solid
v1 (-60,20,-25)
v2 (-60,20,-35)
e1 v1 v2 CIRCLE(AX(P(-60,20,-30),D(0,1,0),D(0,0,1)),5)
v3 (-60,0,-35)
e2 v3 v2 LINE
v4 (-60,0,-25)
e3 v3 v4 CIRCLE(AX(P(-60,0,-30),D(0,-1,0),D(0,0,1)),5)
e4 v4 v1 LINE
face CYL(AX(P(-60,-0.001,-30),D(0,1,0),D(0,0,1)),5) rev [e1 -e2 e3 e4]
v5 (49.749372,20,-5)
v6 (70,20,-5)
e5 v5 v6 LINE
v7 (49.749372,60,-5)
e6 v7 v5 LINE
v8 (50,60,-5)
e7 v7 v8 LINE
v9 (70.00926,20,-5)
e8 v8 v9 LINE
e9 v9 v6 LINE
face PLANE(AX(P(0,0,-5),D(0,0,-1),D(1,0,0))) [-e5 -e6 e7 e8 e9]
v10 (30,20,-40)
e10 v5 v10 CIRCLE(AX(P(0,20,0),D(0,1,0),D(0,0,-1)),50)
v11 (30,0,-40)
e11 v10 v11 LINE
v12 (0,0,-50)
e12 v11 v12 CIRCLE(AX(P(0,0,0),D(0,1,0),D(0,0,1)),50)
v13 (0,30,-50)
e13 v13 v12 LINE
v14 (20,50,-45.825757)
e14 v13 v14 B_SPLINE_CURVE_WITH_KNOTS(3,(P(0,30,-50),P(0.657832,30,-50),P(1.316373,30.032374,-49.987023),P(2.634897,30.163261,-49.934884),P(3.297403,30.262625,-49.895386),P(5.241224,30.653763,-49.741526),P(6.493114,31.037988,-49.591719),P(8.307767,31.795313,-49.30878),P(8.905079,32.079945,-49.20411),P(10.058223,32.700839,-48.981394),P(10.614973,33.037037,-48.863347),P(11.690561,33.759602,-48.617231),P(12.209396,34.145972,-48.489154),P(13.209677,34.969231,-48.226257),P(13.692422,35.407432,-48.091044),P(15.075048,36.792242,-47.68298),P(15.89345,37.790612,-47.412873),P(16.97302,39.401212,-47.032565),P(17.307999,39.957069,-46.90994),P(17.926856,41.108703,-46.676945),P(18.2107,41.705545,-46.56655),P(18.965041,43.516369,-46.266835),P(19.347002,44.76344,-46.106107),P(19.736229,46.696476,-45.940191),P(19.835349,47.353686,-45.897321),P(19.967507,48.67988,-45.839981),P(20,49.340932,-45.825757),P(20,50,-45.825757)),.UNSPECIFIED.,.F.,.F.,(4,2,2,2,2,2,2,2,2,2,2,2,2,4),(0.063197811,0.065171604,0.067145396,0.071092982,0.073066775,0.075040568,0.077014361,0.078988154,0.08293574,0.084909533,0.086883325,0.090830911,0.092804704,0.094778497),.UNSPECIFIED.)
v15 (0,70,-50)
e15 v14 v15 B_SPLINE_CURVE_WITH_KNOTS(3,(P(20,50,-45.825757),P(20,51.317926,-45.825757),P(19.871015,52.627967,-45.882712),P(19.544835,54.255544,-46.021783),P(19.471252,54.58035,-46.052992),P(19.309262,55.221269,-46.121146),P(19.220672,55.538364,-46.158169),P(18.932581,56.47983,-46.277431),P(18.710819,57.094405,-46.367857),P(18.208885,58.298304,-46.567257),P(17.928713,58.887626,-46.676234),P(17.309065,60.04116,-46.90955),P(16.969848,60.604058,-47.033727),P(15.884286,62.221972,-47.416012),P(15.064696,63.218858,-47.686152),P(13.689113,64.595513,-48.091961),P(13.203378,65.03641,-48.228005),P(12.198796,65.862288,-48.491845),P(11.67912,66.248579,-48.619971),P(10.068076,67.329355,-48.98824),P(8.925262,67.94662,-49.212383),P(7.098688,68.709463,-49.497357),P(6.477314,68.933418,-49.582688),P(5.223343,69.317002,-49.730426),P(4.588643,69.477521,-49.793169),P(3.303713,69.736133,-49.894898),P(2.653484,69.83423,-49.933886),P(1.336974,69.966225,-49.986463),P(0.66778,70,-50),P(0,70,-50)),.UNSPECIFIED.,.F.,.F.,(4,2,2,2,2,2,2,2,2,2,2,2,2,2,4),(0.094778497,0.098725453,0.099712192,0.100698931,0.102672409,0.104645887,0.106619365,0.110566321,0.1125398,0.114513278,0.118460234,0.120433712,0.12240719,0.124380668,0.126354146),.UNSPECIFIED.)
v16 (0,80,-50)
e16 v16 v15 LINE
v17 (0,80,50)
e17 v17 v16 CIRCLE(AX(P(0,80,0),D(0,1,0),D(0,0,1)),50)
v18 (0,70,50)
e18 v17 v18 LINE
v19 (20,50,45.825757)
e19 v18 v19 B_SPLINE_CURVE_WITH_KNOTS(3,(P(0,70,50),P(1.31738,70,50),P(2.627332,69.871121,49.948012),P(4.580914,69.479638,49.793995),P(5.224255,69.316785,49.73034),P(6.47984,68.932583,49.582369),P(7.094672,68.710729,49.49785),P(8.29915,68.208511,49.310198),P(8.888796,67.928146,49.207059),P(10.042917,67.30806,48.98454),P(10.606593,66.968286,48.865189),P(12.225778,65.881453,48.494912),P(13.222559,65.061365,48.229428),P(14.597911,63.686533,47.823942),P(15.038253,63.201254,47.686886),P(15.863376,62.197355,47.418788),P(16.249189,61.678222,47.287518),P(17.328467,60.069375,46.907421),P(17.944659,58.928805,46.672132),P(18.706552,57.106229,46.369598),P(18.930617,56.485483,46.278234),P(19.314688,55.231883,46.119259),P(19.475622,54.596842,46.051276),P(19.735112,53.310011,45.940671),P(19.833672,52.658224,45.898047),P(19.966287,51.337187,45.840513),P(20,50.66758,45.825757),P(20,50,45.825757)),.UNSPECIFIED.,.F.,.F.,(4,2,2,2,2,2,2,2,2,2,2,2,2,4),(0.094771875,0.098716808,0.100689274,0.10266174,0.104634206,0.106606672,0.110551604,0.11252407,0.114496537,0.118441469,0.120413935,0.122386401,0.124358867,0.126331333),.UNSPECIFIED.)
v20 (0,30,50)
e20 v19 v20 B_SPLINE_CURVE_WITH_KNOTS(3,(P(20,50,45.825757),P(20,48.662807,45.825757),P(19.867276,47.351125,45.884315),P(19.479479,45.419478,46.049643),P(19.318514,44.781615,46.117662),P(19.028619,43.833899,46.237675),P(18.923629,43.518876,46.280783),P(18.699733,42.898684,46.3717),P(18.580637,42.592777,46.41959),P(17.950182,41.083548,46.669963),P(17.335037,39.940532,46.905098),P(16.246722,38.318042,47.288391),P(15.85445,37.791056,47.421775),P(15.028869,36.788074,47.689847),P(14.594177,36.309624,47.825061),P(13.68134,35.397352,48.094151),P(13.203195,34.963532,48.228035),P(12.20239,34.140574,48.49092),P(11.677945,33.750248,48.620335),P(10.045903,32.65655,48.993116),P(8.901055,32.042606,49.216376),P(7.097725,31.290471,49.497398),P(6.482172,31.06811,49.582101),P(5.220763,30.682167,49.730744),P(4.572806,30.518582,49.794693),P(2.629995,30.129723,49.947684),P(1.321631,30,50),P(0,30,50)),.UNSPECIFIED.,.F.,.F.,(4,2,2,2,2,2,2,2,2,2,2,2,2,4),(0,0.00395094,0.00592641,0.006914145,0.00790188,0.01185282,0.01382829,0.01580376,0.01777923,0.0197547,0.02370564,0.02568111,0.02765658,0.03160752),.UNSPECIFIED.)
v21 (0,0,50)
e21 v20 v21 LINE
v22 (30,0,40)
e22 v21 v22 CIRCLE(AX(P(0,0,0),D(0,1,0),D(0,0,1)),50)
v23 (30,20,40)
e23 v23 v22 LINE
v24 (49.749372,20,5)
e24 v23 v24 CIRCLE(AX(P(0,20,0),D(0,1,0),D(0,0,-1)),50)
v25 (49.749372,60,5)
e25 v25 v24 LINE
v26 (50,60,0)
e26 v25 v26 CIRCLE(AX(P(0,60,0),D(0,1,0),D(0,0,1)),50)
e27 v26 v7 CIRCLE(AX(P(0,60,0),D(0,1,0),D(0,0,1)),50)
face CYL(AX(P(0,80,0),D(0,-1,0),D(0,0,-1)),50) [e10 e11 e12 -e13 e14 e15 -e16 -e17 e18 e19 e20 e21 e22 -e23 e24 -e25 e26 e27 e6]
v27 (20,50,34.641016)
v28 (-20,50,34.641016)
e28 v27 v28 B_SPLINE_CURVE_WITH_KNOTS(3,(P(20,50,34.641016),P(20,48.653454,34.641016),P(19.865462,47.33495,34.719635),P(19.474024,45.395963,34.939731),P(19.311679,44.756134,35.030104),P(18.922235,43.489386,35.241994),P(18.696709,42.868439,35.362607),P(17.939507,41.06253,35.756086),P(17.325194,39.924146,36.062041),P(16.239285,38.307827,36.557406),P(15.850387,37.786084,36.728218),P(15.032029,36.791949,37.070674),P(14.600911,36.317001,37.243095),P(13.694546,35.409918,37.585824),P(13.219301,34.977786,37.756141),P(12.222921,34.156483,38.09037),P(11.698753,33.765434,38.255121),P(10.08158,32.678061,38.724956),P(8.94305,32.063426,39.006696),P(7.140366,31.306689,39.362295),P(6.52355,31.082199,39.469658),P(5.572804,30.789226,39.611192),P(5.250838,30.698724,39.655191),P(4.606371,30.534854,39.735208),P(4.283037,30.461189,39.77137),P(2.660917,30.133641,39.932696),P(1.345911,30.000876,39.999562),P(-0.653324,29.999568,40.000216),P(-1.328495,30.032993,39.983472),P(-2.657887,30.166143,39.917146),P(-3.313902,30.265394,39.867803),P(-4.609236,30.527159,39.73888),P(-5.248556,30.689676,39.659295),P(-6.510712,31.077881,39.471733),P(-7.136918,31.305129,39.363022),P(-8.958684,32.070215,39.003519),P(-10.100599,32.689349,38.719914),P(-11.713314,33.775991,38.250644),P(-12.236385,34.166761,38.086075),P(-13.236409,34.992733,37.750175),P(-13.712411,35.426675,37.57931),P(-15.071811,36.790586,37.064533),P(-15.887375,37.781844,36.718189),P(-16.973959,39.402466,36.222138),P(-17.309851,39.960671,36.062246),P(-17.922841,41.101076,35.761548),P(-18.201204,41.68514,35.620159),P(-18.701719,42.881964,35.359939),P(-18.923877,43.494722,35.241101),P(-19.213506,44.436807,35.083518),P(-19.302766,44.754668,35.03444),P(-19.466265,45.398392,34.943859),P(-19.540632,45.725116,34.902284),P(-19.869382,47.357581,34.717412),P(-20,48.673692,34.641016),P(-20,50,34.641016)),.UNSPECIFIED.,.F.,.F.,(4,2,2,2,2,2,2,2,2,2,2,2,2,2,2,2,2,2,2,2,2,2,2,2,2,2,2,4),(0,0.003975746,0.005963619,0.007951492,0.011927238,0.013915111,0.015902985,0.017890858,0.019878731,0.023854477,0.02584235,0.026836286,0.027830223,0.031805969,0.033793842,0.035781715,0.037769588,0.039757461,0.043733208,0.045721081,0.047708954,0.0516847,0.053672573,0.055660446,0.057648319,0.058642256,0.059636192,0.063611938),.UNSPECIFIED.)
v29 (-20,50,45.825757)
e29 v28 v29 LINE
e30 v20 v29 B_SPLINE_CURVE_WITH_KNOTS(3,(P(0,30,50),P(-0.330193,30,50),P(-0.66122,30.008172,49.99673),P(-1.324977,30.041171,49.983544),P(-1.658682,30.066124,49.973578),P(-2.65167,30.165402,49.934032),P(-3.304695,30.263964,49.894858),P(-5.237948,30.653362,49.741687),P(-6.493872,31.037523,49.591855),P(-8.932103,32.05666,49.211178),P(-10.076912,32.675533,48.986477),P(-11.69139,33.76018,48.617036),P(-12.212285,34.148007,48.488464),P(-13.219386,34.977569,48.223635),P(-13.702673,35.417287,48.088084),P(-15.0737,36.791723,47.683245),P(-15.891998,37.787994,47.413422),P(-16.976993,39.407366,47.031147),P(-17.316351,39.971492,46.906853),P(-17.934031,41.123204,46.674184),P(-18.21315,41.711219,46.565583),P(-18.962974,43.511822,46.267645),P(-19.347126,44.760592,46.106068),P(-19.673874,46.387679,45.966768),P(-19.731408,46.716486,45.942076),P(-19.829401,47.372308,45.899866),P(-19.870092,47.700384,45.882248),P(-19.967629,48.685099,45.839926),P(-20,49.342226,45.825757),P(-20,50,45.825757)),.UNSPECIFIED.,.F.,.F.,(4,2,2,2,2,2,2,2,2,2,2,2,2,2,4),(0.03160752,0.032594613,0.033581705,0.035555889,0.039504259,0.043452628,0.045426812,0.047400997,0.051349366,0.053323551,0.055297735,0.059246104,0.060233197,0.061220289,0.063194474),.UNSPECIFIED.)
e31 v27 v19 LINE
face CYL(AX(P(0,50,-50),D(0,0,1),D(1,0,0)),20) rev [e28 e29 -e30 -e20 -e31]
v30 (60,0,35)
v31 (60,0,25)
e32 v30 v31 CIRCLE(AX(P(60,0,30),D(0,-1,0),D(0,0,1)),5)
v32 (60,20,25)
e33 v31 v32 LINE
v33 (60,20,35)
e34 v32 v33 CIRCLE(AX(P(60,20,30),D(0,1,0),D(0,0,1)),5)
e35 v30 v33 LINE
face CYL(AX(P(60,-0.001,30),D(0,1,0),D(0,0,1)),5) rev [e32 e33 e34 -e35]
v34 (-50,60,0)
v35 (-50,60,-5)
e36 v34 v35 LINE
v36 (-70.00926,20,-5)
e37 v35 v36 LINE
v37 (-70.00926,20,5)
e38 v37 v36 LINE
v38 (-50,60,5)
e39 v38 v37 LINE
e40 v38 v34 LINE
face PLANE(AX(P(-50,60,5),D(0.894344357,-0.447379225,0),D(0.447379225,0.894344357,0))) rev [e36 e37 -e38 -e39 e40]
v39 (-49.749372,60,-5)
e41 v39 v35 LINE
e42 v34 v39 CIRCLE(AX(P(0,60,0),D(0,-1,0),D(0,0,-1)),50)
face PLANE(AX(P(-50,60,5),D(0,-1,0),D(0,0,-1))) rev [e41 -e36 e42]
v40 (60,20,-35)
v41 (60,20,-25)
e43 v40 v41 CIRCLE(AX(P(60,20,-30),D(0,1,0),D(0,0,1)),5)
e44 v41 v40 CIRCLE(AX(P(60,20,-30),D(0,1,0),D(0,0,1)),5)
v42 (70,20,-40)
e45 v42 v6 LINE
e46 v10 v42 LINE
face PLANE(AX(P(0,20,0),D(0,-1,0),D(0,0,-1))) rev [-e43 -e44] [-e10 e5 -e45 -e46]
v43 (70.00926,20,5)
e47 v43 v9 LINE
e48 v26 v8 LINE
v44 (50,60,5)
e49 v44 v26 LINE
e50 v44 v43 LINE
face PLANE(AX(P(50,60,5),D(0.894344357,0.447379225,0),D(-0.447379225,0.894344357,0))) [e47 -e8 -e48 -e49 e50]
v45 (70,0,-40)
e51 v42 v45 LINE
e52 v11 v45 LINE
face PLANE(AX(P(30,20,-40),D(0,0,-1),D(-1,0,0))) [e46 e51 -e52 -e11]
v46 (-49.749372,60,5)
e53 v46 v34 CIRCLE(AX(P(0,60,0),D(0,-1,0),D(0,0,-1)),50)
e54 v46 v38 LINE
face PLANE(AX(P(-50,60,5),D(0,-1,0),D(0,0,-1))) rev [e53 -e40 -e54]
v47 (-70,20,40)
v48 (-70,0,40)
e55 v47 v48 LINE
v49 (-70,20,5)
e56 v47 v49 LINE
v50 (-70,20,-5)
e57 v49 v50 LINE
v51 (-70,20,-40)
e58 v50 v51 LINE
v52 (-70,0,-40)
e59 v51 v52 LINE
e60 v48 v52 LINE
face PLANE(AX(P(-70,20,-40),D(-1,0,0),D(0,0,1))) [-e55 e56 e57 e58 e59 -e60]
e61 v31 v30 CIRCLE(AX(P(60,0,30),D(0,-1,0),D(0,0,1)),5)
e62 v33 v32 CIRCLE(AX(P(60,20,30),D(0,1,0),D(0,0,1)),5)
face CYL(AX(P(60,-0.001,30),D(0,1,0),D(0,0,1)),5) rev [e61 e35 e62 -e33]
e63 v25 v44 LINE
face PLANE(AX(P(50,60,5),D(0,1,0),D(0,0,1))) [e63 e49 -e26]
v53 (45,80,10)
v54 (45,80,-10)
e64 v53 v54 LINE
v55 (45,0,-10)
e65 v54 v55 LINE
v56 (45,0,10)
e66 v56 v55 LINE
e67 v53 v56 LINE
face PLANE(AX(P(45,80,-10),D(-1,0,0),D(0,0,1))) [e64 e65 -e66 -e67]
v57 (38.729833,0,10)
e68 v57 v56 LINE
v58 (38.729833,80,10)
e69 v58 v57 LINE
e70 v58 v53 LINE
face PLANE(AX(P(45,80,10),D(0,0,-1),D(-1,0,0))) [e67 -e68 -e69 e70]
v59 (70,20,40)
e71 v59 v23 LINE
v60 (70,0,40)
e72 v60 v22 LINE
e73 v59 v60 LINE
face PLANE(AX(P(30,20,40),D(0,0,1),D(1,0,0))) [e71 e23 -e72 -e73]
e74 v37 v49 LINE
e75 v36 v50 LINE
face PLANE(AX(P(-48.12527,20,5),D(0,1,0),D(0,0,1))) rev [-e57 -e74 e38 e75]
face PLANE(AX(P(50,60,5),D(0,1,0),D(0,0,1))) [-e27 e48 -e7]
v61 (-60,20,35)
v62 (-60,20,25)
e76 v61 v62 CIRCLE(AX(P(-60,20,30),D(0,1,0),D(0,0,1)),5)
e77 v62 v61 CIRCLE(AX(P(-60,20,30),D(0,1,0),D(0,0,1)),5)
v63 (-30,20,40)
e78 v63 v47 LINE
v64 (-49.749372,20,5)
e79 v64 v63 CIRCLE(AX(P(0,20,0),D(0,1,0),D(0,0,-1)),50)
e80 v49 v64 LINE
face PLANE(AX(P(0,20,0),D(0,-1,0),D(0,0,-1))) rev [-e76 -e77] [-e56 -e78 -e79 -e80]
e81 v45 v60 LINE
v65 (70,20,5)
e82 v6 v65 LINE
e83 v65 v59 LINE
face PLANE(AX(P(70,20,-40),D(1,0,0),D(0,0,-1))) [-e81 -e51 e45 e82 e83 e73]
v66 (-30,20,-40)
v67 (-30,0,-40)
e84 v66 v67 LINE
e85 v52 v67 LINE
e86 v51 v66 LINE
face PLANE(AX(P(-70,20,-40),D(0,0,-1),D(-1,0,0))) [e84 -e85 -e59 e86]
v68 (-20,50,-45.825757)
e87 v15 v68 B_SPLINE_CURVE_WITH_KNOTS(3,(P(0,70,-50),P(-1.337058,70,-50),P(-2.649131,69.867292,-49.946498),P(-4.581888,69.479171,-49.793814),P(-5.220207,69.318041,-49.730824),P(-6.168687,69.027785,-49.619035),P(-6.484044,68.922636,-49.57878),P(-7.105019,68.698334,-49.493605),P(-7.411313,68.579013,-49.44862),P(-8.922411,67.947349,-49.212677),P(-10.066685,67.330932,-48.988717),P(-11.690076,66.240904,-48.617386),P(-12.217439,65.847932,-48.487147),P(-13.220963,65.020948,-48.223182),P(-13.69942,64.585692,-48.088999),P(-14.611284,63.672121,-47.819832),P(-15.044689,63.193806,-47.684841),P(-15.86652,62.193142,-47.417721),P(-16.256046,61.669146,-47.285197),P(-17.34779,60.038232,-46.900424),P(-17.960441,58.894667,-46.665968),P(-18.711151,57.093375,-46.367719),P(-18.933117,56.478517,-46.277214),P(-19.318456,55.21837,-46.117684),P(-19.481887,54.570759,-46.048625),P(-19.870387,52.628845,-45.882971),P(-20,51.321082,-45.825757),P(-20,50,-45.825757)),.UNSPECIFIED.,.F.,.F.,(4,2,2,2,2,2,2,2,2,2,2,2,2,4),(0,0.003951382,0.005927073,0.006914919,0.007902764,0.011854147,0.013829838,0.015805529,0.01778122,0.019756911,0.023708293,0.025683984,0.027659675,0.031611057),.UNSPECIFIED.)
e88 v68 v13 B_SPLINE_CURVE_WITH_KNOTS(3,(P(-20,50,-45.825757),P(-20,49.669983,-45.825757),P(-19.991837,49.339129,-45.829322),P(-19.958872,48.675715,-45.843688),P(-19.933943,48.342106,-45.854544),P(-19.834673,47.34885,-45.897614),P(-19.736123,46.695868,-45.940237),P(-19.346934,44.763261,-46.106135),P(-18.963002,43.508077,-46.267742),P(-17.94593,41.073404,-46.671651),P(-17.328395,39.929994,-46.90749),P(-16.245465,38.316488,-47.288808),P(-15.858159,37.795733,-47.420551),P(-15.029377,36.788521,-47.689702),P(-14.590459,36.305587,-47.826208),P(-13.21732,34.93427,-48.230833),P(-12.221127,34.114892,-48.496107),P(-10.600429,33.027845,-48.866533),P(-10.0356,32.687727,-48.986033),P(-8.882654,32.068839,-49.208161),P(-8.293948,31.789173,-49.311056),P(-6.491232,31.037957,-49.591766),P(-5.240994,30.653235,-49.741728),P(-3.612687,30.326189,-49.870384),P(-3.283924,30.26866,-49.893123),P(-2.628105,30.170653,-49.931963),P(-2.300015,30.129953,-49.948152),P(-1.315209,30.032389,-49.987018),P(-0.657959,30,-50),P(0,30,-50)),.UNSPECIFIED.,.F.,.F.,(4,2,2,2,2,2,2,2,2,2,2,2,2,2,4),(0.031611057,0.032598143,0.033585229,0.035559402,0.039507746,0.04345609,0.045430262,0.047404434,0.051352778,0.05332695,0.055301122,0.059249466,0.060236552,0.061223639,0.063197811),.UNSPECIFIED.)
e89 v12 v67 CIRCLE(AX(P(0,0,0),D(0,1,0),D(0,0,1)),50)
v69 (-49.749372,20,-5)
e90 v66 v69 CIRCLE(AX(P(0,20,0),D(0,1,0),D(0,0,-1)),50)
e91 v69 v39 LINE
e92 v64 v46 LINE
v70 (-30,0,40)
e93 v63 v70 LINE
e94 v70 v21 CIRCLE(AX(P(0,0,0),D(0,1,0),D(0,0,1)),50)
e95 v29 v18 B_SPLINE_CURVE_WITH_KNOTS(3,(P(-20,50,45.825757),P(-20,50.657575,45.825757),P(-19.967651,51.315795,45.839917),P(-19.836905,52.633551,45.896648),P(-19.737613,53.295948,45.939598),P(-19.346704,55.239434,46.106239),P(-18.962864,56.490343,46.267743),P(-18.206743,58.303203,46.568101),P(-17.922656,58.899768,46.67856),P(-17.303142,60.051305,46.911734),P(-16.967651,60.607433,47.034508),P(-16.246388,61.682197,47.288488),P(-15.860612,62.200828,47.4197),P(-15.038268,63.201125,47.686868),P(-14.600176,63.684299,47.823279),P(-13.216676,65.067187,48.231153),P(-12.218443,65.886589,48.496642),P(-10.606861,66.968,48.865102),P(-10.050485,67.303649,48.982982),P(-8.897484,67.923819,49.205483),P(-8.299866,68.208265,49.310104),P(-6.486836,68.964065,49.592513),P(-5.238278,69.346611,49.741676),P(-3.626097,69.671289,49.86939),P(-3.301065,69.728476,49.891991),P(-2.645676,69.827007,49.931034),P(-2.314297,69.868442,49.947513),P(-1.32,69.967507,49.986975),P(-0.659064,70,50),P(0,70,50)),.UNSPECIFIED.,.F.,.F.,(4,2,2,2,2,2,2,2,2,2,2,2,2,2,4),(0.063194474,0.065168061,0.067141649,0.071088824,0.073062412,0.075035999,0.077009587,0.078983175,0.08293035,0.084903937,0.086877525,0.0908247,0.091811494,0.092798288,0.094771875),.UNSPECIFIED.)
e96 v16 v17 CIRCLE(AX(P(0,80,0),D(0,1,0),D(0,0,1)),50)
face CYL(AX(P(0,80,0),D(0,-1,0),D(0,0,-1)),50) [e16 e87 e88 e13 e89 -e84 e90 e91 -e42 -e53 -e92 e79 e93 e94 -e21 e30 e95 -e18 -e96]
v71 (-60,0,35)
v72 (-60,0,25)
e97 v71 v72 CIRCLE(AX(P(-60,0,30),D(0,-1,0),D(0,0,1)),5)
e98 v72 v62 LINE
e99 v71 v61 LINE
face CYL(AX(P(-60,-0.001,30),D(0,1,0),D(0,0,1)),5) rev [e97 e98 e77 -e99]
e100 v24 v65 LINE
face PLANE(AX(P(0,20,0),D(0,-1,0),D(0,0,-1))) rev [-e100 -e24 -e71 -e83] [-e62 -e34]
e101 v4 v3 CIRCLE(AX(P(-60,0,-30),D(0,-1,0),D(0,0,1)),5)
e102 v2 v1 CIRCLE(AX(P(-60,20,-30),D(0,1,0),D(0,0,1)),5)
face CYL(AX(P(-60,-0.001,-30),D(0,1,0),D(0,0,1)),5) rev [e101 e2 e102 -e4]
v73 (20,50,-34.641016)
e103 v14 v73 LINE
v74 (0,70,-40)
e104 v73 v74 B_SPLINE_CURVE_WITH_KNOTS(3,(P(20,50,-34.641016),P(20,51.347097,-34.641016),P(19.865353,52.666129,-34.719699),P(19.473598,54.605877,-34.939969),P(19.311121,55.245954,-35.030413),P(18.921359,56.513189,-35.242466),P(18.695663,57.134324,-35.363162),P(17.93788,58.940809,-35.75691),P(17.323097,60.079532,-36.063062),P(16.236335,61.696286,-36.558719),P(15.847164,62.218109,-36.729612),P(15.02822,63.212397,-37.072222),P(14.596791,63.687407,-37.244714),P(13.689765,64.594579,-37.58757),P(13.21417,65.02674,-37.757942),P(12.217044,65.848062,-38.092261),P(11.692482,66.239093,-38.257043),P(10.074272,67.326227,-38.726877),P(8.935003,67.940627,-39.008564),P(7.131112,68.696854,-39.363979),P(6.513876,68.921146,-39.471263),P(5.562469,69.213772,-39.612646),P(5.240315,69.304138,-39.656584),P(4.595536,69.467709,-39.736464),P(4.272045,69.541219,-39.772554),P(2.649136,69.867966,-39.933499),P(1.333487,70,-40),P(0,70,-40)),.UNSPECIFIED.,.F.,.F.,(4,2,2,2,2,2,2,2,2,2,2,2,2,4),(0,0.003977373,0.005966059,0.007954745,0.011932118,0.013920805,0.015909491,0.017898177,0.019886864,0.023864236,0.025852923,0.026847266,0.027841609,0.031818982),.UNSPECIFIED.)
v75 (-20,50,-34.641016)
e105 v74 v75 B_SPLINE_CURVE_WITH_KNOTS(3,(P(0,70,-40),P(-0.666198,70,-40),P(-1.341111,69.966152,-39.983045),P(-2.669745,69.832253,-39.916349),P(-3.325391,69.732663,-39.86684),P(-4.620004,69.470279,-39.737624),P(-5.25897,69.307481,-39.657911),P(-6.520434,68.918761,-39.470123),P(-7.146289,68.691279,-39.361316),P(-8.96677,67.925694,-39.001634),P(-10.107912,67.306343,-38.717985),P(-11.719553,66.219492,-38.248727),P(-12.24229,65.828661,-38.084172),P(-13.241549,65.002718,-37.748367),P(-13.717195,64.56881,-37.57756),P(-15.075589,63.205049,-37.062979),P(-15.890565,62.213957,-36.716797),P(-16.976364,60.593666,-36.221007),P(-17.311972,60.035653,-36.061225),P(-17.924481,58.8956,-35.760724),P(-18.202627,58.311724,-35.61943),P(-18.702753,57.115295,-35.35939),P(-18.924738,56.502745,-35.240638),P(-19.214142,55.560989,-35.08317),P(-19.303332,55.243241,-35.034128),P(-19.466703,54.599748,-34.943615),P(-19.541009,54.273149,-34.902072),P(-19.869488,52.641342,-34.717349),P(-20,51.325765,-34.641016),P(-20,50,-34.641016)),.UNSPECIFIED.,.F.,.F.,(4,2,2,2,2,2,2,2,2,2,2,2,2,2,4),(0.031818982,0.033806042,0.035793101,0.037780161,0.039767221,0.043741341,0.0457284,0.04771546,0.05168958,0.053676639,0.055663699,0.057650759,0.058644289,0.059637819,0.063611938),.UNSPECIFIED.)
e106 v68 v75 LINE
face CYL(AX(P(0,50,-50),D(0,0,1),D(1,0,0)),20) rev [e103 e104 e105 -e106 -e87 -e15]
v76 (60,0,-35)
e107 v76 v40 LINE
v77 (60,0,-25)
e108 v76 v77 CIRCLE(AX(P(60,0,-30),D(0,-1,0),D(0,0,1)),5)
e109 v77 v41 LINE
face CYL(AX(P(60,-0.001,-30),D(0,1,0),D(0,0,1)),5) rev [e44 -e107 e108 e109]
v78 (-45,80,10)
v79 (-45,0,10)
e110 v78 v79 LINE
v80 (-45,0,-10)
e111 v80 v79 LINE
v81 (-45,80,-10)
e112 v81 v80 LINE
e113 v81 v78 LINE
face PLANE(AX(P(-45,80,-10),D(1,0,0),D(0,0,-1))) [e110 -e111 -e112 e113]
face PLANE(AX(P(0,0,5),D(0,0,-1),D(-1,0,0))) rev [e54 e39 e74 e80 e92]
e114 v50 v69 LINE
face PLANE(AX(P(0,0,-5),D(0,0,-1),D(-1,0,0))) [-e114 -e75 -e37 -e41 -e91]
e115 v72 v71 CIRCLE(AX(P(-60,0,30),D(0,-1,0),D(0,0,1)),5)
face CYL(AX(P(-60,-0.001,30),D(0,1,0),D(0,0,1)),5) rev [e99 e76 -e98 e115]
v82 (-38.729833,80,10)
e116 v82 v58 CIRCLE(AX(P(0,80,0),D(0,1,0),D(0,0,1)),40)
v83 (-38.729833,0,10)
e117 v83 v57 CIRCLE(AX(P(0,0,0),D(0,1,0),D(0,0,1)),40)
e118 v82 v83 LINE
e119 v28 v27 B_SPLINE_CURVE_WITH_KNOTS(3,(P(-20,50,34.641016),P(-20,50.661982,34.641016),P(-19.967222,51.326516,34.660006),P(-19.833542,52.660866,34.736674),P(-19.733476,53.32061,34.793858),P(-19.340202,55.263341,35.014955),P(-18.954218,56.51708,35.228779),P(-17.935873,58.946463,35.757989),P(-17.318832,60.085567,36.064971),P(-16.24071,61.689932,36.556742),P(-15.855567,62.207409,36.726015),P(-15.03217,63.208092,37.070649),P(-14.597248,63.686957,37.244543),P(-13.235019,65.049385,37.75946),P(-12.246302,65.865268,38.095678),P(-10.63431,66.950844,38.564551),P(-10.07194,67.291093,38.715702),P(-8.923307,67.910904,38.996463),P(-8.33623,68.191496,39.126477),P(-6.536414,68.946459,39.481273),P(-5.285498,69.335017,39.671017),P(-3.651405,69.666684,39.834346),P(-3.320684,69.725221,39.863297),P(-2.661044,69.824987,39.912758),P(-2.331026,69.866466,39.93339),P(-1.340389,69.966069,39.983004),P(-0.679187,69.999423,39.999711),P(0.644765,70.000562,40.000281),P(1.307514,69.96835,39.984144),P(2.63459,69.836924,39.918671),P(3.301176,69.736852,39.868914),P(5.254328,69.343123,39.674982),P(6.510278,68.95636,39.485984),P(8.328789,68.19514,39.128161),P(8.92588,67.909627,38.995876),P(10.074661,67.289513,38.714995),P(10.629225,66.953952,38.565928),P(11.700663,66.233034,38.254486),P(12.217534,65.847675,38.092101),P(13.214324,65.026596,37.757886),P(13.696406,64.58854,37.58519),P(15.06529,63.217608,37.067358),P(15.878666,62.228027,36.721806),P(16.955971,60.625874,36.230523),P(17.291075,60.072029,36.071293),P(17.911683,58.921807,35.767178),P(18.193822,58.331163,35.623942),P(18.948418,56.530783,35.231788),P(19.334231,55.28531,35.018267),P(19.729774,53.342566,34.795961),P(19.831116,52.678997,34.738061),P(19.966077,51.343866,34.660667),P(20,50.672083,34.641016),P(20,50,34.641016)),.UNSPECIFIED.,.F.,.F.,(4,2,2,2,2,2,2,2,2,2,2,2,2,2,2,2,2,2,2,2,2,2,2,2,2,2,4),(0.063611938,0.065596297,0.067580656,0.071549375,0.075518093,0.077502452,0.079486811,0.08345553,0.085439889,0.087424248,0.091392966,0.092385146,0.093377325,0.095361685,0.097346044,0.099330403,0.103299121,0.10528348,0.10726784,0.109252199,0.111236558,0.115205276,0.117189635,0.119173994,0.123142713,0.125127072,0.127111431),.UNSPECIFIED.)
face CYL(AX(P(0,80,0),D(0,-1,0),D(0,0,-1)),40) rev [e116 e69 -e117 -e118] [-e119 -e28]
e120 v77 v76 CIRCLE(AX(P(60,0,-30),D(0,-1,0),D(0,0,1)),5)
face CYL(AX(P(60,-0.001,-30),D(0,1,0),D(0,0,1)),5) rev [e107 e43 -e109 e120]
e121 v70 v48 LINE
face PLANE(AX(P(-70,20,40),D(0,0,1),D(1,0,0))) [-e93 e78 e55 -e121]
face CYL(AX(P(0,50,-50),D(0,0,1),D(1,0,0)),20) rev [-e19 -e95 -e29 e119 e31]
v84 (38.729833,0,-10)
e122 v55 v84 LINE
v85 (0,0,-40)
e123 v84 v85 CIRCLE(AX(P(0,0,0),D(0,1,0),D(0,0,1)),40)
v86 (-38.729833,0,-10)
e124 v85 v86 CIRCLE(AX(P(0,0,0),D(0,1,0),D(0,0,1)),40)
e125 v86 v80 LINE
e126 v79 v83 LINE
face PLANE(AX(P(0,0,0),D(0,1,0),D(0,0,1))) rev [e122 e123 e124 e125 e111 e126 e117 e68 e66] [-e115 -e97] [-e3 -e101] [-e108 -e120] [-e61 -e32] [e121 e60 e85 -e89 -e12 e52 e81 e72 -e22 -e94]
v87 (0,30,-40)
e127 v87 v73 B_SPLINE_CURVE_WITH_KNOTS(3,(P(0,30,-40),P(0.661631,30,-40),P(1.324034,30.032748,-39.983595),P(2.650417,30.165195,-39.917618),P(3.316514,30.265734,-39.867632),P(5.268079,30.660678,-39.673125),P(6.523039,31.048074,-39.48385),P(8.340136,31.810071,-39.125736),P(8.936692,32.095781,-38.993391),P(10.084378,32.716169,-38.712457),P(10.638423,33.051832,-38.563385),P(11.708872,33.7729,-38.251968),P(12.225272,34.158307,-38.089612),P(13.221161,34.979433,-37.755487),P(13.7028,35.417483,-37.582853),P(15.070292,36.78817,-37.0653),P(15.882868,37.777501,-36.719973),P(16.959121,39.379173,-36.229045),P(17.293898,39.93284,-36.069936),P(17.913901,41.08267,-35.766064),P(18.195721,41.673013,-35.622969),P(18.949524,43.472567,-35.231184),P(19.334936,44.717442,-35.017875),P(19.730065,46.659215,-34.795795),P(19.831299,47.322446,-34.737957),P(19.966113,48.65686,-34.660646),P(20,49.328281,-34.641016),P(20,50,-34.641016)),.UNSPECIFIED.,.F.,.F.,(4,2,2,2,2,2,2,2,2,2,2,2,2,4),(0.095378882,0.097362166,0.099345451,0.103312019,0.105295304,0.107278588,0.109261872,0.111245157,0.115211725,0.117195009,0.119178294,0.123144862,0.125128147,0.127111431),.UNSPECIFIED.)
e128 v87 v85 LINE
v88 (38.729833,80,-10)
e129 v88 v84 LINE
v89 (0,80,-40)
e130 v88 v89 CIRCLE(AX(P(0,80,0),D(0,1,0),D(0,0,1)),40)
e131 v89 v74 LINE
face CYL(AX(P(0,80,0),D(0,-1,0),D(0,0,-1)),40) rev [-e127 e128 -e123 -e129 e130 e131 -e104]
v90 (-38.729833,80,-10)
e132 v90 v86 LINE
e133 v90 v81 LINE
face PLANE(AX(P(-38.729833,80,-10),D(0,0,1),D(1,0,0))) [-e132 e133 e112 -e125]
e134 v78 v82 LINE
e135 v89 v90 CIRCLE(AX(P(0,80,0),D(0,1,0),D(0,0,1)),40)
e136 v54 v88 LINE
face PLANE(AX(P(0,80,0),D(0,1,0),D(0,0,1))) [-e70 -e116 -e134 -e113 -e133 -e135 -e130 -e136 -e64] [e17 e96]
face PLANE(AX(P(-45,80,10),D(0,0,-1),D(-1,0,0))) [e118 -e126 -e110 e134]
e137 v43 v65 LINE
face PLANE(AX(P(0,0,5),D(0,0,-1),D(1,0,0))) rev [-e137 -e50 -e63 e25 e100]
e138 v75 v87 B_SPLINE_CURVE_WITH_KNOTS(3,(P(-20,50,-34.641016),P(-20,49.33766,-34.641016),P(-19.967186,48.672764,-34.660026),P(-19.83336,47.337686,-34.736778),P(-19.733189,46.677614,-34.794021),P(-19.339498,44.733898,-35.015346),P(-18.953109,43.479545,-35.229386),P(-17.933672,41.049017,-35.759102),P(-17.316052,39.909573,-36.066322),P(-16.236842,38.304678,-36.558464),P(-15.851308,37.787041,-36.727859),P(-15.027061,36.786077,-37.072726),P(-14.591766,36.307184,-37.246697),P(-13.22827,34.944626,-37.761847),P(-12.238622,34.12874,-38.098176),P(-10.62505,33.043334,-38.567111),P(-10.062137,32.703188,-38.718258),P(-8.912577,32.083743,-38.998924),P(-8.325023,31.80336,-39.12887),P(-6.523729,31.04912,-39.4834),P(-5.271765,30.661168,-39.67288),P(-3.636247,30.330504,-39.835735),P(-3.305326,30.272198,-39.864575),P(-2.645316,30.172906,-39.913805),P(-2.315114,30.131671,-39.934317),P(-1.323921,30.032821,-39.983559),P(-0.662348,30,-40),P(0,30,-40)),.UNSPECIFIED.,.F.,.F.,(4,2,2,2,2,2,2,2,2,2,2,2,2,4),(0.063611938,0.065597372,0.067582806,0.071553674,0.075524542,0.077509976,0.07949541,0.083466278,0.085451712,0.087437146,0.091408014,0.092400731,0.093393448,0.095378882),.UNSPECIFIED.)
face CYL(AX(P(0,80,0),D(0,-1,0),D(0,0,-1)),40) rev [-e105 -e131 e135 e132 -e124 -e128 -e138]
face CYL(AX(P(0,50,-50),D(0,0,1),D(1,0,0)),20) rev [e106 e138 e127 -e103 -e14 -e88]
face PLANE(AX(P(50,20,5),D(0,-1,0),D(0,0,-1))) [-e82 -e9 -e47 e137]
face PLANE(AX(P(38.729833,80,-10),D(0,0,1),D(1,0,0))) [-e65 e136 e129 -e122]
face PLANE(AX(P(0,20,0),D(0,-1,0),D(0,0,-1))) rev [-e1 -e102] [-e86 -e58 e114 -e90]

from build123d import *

# Parameters (mm, degrees)
HOUSING_PROFILE_SKETCH_R   = 50
HOUSING_BODY_DEPTH         = 80
BASE_FLANGE_DEPTH          = 20
SUPPORT_RIB_DEPTH          = 5
CROSS_BORE_40_DEPTH        = 118.478919467
CROSS_BORE_40_DEPTH_BACK   = 118.478919467
CROSS_BORE_SKETCH_R        = 20
MOUNTING_HOLES_4X_10_REACH = 106.887
MOUNTING_HOLES_SKETCH_R    = 5


with BuildPart() as part:
    # Housing Profile Sketch → Housing Body (new body)
    with BuildSketch(Plane(origin=(0, 0, 0), x_dir=(1, 0, 0), z_dir=(0, 1, 0))):
        with Locations(Location((0, 0, 0), (0, 0, 270))):
            Circle(HOUSING_PROFILE_SKETCH_R)
        with BuildLine():
            Line((-38.729833462, 10), (-45, 10))
            Line((-45, 10), (-45, -10))
            Line((-45, -10), (-38.729833462, -10))
            ThreePointArc((-38.729833462, -10), (0, -40), (38.729833462, -10))
            Line((38.729833462, -10), (45, -10))
            Line((45, -10), (45, 10))
            Line((45, 10), (38.729833462, 10))
            ThreePointArc((38.729833462, 10), (0, 40), (-38.729833462, 10))
        make_face(mode=Mode.SUBTRACT)
    extrude(amount=HOUSING_BODY_DEPTH)

    # Base Flange Sketch → Base Flange (add)
    with BuildSketch(Plane.XZ):
        with BuildLine():
            Line((30, 40), (70, 40))
            Line((70, 40), (70, -40))
            Line((70, -40), (30, -40))
            ThreePointArc((30, -40), (50, 0), (30, 40))
        make_face()
        with BuildLine():
            Line((-70, -40), (-30, -40))
            ThreePointArc((-30, -40), (-50, 0), (-30, 40))
            Line((-30, 40), (-70, 40))
            Line((-70, 40), (-70, -40))
        make_face()
    extrude(amount=-BASE_FLANGE_DEPTH)

    # Support Rib Sketch → Support Rib (add, symmetric)
    with BuildSketch(Plane.XY):
        Polygon((-50, 60), (-70.009260239, 20), (-50, 20), (-48.125269869, 20), (-48.125269869, 60), align=None)
    support_rib = extrude(amount=SUPPORT_RIB_DEPTH, both=True)

    # Support Rib Mirror: Support Rib across plane
    add(support_rib.mirror(Plane(origin=(0, 0, 0), x_dir=(0, 0, 1), z_dir=(1, 0, 0))))

    # Cross Bore Sketch → Cross Bore Ø40 (cut, two sides: drawn at the far end of the back side and taken through both)
    with BuildSketch(Plane.XY.offset(-CROSS_BORE_40_DEPTH_BACK)):
        with Locations((0, 50)):
            Circle(CROSS_BORE_SKETCH_R)
    extrude(amount=CROSS_BORE_40_DEPTH + CROSS_BORE_40_DEPTH_BACK, mode=Mode.SUBTRACT)

    # Mounting Holes Sketch → Mounting Holes 4xØ10 (cut, up to next)
    with BuildSketch(Plane(origin=(0, 20, 0), x_dir=(1, 0, 0), z_dir=(0, 1, 0)), mode=Mode.PRIVATE) as mounting_holes_4x_10_sk1:
        with Locations(Location((-60, 30, 0), (0, 0, 270))):
            Circle(MOUNTING_HOLES_SKETCH_R)
    mounting_holes_4x_10_tool1 = extrude(mounting_holes_4x_10_sk1.sketch, amount=-MOUNTING_HOLES_4X_10_REACH, mode=Mode.PRIVATE) & part.part
    # Mounting Holes Sketch → Mounting Holes 4xØ10 (cut, up to next)
    with BuildSketch(Plane(origin=(0, 20, 0), x_dir=(1, 0, 0), z_dir=(0, 1, 0)), mode=Mode.PRIVATE) as mounting_holes_4x_10_sk2:
        with Locations(Location((60, 30, 0), (0, 0, 270))):
            Circle(MOUNTING_HOLES_SKETCH_R)
    mounting_holes_4x_10_tool2 = extrude(mounting_holes_4x_10_sk2.sketch, amount=-MOUNTING_HOLES_4X_10_REACH, mode=Mode.PRIVATE) & part.part
    # Mounting Holes Sketch → Mounting Holes 4xØ10 (cut, up to next)
    with BuildSketch(Plane(origin=(0, 20, 0), x_dir=(1, 0, 0), z_dir=(0, 1, 0)), mode=Mode.PRIVATE) as mounting_holes_4x_10_sk3:
        with Locations(Location((60, -30, 0), (0, 0, 270))):
            Circle(MOUNTING_HOLES_SKETCH_R)
    mounting_holes_4x_10_tool3 = extrude(mounting_holes_4x_10_sk3.sketch, amount=-MOUNTING_HOLES_4X_10_REACH, mode=Mode.PRIVATE) & part.part
    # Mounting Holes Sketch → Mounting Holes 4xØ10 (cut, up to next)
    with BuildSketch(Plane(origin=(0, 20, 0), x_dir=(1, 0, 0), z_dir=(0, 1, 0)), mode=Mode.PRIVATE) as mounting_holes_4x_10_sk4:
        with Locations(Location((-60, -30, 0), (0, 0, 270))):
            Circle(MOUNTING_HOLES_SKETCH_R)
    mounting_holes_4x_10_tool4 = extrude(mounting_holes_4x_10_sk4.sketch, amount=-MOUNTING_HOLES_4X_10_REACH, mode=Mode.PRIVATE) & part.part
    add(mounting_holes_4x_10_tool1.solids().sort_by_distance((-60, 20, -30))[0], mode=Mode.SUBTRACT)
    add(mounting_holes_4x_10_tool2.solids().sort_by_distance((60, 20, -30))[0], mode=Mode.SUBTRACT)
    add(mounting_holes_4x_10_tool3.solids().sort_by_distance((60, 20, 30))[0], mode=Mode.SUBTRACT)
    add(mounting_holes_4x_10_tool4.solids().sort_by_distance((-60, 20, 30))[0], mode=Mode.SUBTRACT)


solid = part.part
